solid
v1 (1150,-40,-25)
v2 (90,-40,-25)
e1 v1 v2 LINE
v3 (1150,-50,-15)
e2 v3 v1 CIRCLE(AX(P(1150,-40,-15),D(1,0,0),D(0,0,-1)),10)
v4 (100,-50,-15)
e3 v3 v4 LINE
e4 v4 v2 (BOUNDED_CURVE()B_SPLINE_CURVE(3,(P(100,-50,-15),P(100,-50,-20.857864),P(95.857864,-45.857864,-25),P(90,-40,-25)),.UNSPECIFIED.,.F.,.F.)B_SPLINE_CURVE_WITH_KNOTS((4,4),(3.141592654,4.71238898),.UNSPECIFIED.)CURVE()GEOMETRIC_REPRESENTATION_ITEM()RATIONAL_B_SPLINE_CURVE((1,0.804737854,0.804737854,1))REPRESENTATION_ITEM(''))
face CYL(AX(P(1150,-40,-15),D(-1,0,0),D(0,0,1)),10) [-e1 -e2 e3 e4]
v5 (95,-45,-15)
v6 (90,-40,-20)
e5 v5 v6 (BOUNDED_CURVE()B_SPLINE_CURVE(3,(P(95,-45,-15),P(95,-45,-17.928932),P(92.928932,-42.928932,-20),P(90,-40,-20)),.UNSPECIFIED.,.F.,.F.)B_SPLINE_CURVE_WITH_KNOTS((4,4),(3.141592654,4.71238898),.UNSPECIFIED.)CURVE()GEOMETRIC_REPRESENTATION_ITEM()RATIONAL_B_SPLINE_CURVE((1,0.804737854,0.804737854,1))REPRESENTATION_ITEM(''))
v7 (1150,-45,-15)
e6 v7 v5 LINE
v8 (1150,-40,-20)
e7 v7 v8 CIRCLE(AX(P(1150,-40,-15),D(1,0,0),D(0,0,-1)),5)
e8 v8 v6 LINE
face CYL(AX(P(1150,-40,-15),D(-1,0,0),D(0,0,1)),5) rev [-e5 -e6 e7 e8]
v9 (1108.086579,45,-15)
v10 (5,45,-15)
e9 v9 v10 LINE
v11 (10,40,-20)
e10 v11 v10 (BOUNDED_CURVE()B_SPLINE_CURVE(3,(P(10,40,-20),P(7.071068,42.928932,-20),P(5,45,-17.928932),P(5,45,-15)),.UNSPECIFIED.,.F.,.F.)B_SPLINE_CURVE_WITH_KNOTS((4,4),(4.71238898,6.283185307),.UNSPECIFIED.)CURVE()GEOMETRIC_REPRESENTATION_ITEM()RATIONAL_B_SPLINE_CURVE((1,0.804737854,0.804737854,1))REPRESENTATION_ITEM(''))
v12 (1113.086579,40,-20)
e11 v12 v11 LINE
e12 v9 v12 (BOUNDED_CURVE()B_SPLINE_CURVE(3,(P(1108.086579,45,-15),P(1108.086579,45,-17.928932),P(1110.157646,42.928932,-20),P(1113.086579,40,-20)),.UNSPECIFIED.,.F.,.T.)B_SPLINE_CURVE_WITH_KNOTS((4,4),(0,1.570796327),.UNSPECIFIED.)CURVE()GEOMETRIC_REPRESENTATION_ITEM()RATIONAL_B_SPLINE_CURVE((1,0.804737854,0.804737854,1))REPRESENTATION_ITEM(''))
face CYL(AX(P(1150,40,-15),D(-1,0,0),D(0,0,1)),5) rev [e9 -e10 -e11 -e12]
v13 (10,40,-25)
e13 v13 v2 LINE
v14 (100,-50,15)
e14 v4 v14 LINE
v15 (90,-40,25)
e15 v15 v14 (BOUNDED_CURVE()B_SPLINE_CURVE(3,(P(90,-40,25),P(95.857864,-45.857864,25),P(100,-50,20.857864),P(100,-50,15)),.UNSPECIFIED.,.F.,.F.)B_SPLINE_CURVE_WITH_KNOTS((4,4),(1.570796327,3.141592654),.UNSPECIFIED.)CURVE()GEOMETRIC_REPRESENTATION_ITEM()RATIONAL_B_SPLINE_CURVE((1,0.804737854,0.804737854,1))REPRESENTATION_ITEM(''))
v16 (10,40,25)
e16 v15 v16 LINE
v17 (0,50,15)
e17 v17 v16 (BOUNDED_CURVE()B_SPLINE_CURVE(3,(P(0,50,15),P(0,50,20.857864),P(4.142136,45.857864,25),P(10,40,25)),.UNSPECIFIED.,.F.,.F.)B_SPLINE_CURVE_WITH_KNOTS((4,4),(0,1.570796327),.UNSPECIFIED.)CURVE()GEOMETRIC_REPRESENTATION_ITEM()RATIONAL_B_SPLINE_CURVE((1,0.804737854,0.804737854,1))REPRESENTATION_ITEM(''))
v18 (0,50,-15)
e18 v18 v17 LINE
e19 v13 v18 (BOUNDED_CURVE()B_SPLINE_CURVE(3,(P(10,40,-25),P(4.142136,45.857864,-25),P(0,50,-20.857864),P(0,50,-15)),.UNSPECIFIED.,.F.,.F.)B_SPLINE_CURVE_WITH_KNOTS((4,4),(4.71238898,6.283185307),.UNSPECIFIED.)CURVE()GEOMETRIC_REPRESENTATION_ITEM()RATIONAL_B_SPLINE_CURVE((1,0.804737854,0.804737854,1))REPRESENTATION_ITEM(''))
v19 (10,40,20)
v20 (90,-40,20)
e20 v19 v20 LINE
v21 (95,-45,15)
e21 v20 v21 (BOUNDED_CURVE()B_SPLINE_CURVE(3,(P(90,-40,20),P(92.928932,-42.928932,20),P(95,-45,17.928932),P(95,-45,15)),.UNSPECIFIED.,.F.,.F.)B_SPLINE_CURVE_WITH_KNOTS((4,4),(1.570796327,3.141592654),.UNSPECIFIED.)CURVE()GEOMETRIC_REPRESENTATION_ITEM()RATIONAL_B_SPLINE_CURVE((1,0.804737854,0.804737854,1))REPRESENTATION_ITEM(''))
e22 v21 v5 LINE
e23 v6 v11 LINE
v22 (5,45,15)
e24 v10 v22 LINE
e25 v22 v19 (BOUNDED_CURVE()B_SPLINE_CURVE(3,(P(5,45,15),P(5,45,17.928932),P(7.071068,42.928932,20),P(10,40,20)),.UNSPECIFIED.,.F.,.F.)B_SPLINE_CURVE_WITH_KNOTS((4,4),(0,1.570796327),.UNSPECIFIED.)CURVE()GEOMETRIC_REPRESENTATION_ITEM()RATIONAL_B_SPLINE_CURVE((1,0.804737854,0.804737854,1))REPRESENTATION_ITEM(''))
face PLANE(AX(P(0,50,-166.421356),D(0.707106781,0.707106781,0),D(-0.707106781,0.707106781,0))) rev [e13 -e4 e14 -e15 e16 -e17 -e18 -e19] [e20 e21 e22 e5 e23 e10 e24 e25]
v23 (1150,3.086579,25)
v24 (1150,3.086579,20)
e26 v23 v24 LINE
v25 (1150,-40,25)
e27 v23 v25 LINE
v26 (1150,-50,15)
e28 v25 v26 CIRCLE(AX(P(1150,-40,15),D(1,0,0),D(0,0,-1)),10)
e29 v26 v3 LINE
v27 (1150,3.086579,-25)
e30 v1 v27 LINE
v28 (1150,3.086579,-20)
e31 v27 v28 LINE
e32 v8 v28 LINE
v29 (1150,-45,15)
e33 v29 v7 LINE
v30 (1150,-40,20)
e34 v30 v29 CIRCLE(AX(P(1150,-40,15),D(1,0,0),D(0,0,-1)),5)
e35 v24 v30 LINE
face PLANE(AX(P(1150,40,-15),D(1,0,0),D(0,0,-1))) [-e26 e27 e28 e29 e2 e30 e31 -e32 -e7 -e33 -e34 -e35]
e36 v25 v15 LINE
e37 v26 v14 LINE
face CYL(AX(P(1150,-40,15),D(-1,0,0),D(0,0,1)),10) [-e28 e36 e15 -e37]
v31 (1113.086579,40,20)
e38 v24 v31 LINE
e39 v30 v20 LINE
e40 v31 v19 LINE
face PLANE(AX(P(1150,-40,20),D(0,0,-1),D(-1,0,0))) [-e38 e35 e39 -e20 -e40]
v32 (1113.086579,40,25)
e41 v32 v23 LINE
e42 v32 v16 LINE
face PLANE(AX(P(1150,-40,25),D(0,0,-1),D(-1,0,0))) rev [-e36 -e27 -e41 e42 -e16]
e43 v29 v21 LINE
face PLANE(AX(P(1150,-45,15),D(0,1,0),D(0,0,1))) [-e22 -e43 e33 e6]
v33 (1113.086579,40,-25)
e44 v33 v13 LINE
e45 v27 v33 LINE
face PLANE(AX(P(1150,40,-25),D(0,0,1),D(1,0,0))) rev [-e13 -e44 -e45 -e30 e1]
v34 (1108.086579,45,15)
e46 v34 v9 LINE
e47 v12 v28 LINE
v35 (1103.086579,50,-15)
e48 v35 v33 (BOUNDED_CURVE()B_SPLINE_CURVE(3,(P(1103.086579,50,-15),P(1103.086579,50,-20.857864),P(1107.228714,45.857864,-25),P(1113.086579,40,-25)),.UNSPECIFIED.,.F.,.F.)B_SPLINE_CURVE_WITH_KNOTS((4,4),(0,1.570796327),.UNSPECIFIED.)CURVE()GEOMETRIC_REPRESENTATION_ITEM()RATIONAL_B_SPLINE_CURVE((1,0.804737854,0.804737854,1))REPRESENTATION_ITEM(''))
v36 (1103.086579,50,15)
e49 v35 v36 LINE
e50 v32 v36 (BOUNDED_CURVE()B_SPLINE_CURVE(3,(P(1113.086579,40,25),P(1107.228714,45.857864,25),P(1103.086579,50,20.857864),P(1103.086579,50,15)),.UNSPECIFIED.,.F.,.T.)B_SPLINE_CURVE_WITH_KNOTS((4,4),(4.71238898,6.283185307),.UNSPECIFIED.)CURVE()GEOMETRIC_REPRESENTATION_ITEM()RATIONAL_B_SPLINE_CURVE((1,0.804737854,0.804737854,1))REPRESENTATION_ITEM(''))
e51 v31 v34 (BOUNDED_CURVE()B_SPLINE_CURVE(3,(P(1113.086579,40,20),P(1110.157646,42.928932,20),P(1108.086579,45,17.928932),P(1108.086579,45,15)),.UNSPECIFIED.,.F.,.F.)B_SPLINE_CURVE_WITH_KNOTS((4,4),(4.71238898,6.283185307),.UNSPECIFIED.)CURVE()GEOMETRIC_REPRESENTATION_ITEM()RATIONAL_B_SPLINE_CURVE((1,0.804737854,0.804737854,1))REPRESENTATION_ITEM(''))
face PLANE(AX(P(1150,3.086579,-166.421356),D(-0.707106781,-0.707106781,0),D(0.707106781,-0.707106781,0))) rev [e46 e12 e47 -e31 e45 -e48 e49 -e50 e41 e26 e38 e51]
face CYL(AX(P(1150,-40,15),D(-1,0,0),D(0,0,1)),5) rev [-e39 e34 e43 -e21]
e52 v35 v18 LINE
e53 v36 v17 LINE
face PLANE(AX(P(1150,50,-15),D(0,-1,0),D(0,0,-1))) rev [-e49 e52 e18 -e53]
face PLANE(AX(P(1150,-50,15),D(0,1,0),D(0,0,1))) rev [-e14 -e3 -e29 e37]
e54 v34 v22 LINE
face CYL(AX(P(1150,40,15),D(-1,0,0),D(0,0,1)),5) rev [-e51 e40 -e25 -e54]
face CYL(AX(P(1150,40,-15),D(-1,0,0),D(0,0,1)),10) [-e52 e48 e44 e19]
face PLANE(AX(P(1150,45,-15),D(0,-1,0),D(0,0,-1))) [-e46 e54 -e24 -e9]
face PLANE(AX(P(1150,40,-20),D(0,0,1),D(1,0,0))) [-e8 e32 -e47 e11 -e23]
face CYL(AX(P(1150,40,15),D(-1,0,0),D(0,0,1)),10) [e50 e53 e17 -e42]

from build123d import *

# Parameters (mm, degrees)
F_100_X_50_X_5_1_DEPTH = 1150
CUT_EXTRUDE_1_REACH    = 1159.854


with BuildPart() as part:
    # Sketch11 → 矩形管 100 X 50 X 5(1) (new body)
    with BuildSketch(Plane(origin=(0, 0, 0), x_dir=(0, 0, -1), z_dir=(1, 0, 0))):
        with BuildLine():
            Line((-15, -50), (15, -50))
            ThreePointArc((15, -50), (22.071067812, -47.071067812), (25, -40))
            Line((25, -40), (25, 40))
            ThreePointArc((25, 40), (22.071067812, 47.071067812), (15, 50))
            Line((15, 50), (-15, 50))
            ThreePointArc((-15, 50), (-22.071067812, 47.071067812), (-25, 40))
            Line((-25, 40), (-25, -40))
            ThreePointArc((-25, -40), (-22.071067812, -47.071067812), (-15, -50))
        make_face()
        with BuildLine():
            Line((-15, -45), (15, -45))
            ThreePointArc((15, -45), (18.535533906, -43.535533906), (20, -40))
            Line((20, -40), (20, 40))
            ThreePointArc((20, 40), (18.535533906, 43.535533906), (15, 45))
            Line((15, 45), (-15, 45))
            ThreePointArc((-15, 45), (-18.535533906, 43.535533906), (-20, 40))
            Line((-20, 40), (-20, -40))
            ThreePointArc((-20, -40), (-18.535533906, -43.535533906), (-15, -45))
        make_face(mode=Mode.SUBTRACT)
    extrude(amount=F_100_X_50_X_5_1_DEPTH)

    # 切除-拉伸1: up to this face of the body (flat: up to its plane)
    cut_extrude_1_end = Plane(part.part.faces().sort_by_distance((575, 0, -25))[0])
    # 草图2 → 切除-拉伸1 (cut, up to the picked face)
    with BuildSketch(Plane(origin=(0, 75, 25), x_dir=(1, 0, 0), z_dir=(0, 0, 1)), mode=Mode.PRIVATE) as cut_extrude_1_sk1:
        Polygon((0, -25), (100, -125), (0, -125), align=None)
    cut_extrude_1_tool1 = split(extrude(cut_extrude_1_sk1.sketch, amount=-CUT_EXTRUDE_1_REACH, mode=Mode.PRIVATE), bisect_by=cut_extrude_1_end, keep=Keep.BOTH, mode=Mode.PRIVATE)
    # 草图2 → 切除-拉伸1 (cut, up to the picked face)
    with BuildSketch(Plane(origin=(0, 75, 25), x_dir=(1, 0, 0), z_dir=(0, 0, 1)), mode=Mode.PRIVATE) as cut_extrude_1_sk2:
        Polygon((1150, -71.913421349), (1103.086578651, -25), (1150, -25), align=None)
    cut_extrude_1_tool2 = split(extrude(cut_extrude_1_sk2.sketch, amount=-CUT_EXTRUDE_1_REACH, mode=Mode.PRIVATE), bisect_by=cut_extrude_1_end, keep=Keep.BOTH, mode=Mode.PRIVATE)
    add(cut_extrude_1_tool1.solids().sort_by(Axis((33.333333, -16.666667, 25), (0, 0, -1)))[0], mode=Mode.SUBTRACT)
    add(cut_extrude_1_tool2.solids().sort_by(Axis((1134.362193, 34.362193, 25), (0, 0, -1)))[0], mode=Mode.SUBTRACT)


solid = part.part
